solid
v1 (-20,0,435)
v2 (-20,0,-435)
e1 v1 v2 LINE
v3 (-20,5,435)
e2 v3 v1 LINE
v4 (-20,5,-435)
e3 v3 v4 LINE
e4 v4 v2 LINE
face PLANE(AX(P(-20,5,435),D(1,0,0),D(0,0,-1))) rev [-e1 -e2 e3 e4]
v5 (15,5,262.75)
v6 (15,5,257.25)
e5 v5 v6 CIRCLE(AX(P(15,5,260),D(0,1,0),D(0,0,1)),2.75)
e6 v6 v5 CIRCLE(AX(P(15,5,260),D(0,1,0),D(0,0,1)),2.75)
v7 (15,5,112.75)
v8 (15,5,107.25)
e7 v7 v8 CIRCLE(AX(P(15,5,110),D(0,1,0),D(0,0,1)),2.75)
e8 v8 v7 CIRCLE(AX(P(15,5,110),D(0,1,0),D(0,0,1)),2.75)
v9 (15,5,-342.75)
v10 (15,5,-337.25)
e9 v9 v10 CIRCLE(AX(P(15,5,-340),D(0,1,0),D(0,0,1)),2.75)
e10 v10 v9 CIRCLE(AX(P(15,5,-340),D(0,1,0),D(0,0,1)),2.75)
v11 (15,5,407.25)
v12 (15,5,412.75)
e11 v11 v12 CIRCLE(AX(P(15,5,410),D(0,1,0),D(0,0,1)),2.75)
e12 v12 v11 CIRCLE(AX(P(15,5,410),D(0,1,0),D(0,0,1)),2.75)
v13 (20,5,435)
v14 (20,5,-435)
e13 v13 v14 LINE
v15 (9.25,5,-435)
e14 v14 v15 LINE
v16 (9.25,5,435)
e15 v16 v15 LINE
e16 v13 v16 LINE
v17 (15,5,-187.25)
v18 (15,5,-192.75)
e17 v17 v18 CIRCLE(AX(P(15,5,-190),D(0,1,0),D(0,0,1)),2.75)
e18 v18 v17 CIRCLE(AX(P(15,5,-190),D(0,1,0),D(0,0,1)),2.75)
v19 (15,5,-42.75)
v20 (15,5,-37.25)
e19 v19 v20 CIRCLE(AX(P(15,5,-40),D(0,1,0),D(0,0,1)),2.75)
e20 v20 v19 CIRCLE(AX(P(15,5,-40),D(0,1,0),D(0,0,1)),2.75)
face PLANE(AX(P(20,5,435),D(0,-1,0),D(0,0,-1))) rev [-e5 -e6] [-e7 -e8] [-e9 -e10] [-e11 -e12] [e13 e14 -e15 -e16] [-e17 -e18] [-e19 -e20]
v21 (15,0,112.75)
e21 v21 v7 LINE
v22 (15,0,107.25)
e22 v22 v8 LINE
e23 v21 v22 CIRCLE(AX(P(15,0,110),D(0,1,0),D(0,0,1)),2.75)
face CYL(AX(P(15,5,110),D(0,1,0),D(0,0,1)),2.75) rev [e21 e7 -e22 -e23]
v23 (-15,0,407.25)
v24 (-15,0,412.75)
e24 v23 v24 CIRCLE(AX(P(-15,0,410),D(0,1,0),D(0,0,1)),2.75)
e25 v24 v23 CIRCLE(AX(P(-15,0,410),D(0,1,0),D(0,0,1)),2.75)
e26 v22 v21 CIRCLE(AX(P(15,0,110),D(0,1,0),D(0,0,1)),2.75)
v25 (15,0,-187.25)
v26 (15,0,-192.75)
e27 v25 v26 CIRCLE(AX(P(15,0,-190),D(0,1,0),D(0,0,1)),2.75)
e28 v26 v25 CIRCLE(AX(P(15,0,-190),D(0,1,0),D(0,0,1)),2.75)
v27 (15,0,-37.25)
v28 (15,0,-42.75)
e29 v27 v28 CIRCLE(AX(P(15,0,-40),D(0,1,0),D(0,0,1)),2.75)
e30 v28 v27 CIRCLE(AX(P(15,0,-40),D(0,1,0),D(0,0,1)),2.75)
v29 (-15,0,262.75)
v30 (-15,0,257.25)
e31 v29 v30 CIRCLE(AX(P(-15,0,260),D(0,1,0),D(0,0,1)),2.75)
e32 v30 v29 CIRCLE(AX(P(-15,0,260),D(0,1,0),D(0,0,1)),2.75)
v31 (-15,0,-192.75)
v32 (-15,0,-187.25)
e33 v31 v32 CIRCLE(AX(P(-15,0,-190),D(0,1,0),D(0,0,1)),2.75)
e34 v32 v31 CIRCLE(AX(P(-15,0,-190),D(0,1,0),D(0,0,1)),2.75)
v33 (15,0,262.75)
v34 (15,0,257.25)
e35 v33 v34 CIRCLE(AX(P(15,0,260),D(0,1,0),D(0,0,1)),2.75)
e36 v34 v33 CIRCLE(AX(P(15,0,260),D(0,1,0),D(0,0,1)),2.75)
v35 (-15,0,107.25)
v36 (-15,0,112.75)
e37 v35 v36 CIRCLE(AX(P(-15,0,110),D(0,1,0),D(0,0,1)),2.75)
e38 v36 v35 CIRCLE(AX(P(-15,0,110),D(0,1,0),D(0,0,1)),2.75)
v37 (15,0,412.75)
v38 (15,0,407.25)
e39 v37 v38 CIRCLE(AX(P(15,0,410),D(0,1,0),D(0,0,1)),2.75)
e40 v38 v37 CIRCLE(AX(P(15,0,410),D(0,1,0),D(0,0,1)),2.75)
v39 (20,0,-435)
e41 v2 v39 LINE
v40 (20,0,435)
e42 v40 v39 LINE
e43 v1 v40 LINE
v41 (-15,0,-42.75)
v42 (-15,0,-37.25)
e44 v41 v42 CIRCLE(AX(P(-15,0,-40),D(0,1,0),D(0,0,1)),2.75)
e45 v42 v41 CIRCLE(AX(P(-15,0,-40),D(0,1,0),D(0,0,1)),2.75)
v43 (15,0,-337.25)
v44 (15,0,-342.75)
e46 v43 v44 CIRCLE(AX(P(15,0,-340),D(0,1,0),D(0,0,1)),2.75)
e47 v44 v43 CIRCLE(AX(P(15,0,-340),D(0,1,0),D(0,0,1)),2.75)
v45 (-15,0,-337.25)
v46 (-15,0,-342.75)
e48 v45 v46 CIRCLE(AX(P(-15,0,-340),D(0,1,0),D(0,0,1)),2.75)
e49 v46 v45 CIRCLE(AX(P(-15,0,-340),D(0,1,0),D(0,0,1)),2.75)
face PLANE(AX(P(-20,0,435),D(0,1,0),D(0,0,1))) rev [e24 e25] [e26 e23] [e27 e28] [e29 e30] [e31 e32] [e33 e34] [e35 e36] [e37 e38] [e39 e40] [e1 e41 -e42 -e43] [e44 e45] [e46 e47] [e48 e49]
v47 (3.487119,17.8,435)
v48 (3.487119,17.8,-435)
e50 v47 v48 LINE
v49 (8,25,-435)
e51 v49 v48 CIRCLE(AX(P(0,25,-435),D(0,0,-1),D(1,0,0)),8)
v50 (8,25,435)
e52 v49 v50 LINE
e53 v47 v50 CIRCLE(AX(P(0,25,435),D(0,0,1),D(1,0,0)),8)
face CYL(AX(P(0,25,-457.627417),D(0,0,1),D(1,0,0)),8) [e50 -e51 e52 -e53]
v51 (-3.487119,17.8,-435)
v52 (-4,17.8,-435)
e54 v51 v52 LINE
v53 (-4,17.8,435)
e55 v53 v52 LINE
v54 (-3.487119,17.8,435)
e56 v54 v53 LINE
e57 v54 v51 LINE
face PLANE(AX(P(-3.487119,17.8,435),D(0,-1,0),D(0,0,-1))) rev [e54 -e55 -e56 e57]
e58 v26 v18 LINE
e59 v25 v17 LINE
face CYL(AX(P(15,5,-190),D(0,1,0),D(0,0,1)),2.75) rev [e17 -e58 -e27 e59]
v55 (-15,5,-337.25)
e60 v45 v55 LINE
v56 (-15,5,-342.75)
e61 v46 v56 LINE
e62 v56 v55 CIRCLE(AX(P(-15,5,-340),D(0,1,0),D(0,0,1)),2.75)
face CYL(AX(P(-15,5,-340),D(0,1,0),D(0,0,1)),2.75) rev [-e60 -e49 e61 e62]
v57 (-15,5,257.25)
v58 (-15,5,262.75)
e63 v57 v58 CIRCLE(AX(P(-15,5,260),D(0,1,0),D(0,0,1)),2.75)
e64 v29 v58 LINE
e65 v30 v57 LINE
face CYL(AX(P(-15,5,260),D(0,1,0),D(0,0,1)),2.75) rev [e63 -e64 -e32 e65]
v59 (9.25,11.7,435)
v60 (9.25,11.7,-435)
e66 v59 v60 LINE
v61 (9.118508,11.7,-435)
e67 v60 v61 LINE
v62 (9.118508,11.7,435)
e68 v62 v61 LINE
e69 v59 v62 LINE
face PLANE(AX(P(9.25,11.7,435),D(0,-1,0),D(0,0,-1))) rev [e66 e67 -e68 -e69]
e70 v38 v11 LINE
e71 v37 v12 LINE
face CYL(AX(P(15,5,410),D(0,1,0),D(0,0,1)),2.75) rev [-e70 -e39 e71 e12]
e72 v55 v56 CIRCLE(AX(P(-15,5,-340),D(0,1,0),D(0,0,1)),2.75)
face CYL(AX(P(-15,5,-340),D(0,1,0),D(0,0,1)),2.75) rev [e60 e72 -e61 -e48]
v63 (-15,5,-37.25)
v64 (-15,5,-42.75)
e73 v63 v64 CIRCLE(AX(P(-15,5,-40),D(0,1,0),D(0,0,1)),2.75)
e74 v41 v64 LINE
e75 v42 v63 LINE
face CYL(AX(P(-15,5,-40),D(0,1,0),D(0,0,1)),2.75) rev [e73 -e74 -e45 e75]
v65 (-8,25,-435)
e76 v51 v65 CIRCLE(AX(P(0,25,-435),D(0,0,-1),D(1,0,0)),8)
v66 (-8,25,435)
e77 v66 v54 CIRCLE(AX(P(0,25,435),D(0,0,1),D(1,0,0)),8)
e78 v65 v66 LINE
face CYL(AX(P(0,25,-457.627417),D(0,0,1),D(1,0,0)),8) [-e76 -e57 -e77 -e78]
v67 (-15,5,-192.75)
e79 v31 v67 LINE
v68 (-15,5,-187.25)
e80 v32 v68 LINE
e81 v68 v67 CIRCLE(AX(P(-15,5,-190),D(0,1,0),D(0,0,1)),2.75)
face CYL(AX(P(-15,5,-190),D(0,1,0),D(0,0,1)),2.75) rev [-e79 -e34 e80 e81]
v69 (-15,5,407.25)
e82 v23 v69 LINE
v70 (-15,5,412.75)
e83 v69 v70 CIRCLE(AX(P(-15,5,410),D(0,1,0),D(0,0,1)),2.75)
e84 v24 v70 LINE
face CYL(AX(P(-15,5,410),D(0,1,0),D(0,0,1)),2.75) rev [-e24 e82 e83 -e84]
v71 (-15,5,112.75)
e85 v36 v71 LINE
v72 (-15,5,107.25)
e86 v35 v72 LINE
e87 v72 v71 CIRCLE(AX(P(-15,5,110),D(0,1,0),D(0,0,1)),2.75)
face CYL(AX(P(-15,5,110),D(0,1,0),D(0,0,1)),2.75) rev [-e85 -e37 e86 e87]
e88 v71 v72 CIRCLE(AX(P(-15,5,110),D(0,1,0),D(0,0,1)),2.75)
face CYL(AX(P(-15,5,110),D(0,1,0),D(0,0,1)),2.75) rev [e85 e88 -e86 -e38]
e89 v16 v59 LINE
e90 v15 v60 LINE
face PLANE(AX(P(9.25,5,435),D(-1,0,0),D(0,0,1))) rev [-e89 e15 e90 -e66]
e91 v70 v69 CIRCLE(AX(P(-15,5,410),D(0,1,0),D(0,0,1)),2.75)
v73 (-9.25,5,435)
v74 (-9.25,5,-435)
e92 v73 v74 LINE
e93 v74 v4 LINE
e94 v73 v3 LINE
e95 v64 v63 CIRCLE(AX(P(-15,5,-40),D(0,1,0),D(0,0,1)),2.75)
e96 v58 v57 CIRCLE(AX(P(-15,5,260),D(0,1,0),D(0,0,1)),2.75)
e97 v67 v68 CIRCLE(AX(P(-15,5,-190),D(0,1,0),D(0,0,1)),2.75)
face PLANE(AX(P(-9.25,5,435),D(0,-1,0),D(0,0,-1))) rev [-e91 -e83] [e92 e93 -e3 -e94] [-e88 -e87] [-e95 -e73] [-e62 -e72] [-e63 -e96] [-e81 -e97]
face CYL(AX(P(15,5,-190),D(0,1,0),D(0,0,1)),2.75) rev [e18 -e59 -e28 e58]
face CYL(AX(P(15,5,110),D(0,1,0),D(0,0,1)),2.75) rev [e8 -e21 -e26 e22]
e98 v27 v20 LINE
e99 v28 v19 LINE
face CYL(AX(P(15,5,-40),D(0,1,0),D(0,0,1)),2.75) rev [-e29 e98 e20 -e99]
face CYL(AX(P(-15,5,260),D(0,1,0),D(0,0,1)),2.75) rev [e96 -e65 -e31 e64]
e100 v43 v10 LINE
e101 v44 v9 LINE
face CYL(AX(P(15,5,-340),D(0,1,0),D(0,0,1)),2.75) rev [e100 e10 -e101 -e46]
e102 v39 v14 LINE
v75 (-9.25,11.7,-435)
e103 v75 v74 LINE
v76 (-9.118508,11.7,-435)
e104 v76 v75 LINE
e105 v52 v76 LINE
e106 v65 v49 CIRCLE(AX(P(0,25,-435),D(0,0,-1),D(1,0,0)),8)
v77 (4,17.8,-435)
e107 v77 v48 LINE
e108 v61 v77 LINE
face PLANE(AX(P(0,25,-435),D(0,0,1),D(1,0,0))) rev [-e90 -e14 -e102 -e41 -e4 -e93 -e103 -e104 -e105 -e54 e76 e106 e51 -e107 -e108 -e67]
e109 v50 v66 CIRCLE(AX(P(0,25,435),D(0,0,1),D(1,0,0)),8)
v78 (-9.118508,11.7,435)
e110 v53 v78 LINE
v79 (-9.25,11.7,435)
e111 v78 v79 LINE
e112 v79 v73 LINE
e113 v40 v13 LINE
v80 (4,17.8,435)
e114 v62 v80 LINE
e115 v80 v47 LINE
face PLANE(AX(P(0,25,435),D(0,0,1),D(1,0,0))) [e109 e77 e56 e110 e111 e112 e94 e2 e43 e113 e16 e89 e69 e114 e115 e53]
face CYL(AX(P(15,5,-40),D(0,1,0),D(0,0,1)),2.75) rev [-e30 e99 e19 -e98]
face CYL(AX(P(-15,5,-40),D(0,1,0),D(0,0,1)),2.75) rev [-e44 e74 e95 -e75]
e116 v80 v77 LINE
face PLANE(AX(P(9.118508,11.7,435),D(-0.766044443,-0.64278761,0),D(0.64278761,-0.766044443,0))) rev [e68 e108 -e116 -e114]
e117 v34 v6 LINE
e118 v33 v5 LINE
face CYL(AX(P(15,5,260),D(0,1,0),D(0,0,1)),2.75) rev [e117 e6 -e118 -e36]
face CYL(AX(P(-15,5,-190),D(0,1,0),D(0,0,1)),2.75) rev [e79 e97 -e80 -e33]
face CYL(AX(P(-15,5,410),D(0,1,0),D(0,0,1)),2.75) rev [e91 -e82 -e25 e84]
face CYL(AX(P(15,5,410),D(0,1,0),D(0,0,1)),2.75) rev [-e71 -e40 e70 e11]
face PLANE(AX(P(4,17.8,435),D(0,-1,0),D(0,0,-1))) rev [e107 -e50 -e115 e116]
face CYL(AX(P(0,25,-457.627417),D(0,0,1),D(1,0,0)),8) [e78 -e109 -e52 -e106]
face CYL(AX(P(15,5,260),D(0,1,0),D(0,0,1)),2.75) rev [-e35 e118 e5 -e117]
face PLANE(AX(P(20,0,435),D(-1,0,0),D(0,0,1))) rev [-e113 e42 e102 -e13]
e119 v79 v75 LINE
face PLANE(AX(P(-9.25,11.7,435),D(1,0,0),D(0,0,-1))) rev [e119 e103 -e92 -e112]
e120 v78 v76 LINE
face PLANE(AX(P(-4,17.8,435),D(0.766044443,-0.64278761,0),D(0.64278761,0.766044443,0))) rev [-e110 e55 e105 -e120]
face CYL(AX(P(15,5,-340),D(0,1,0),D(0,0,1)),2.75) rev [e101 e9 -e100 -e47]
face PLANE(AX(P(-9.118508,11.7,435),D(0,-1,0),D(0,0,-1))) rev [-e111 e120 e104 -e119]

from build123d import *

# Parameters (mm, degrees)
EXTRUDE_1_DEPTH                  = 435
EXTRUDE_2_DEPTH                  = 870
HOLE_WIZARD_5_5_5_5_1_AT_2_COUNT = 2
HOLE_WIZARD_5_5_5_5_1_AT_2_PITCH = 30
PATTERN_LINEAR_1_COUNT           = 6
PATTERN_LINEAR_1_PITCH           = 150


with BuildPart() as part:
    # 草图1 → 凸台-拉伸1 (new, symmetric)
    with BuildSketch(Plane.XY):
        with BuildLine():
            Line((-9.25, 11.7), (-9.25, 5))
            Line((-9.25, 5), (-20, 5))
            Line((-20, 5), (-20, 0))
            Line((-20, 0), (20, 0))
            Line((20, 0), (20, 5))
            Line((20, 5), (9.25, 5))
            Line((9.25, 5), (9.25, 11.7))
            Line((9.25, 11.7), (9.11850775, 11.7))
            Line((9.11850775, 11.7), (4, 17.8))
            Line((4, 17.8), (3.487119155, 17.8))
            ThreePointArc((3.487119155, 17.8), (0, 17), (-3.487119155, 17.8))
            Line((-3.487119155, 17.8), (-4, 17.8))
            Line((-4, 17.8), (-9.11850775, 11.7))
            Line((-9.11850775, 11.7), (-9.25, 11.7))
        make_face()
    extrude(amount=EXTRUDE_1_DEPTH, both=True)

    # 草图2 → 凸台-拉伸2 (add)
    with BuildSketch(Plane.XY.offset(435)):
        with BuildLine():
            ThreePointArc((3.487119155, 17.8), (0, 33), (-3.487119155, 17.8))
            ThreePointArc((-3.487119155, 17.8), (0, 17), (3.487119155, 17.8))
        make_face()
    extrude(amount=-EXTRUDE_2_DEPTH)

    # 草图3 → Ø5.5 (5.5) 直径孔1 (revolve, cut)
    with BuildSketch(Plane(origin=(15, 5, 410), x_dir=(0, 0, 1), z_dir=(1, 0, 0))):
        Polygon((0, 0), (0, 17.19771324), (2.75, 15.61), (2.75, 0), align=None)
    hole_wizard_5_5_5_5_1 = revolve(axis=Axis((15, 11.35, 410), (0, -1, 0)), mode=Mode.SUBTRACT)

    # Ø5.5 (5.5) 直径孔1 at 2: Ø5.5 (5.5) 直径孔1 ×2
    with Locations(*[(-i * HOLE_WIZARD_5_5_5_5_1_AT_2_PITCH, 0, 0) for i in range(1, HOLE_WIZARD_5_5_5_5_1_AT_2_COUNT)]):
        add(hole_wizard_5_5_5_5_1, mode=Mode.SUBTRACT)

    # 阵列(线性)1: Ø5.5 (5.5) 直径孔1 ×6
    with Locations(*[(0, 0, -i * PATTERN_LINEAR_1_PITCH) for i in range(1, PATTERN_LINEAR_1_COUNT)]):
        add(hole_wizard_5_5_5_5_1, mode=Mode.SUBTRACT)

    # 阵列(线性)1 copy 1 sketch → 阵列(线性)1 copy 1 (revolve, cut)
    with BuildSketch(Plane(origin=(-15, 5, 260), x_dir=(0, 0, 1), z_dir=(1, 0, 0))):
        Polygon((0, 0), (0, 17.19771324), (2.75, 15.61), (2.75, 0), align=None)
    revolve(axis=Axis((-15, 11.35, 260), (0, -1, 0)), mode=Mode.SUBTRACT)

    # 阵列(线性)1 copy 2 sketch → 阵列(线性)1 copy 2 (revolve, cut)
    with BuildSketch(Plane(origin=(-15, 5, 110), x_dir=(0, 0, 1), z_dir=(1, 0, 0))):
        Polygon((0, 0), (0, 17.19771324), (2.75, 15.61), (2.75, 0), align=None)
    revolve(axis=Axis((-15, 11.35, 110), (0, -1, 0)), mode=Mode.SUBTRACT)

    # 阵列(线性)1 copy 3 sketch → 阵列(线性)1 copy 3 (revolve, cut)
    with BuildSketch(Plane(origin=(-15, 5, -40), x_dir=(0, 0, 1), z_dir=(1, 0, 0))):
        Polygon((0, 0), (0, 17.19771324), (2.75, 15.61), (2.75, 0), align=None)
    revolve(axis=Axis((-15, 11.35, -40), (0, -1, 0)), mode=Mode.SUBTRACT)

    # 阵列(线性)1 copy 4 sketch → 阵列(线性)1 copy 4 (revolve, cut)
    with BuildSketch(Plane(origin=(-15, 5, -190), x_dir=(0, 0, 1), z_dir=(1, 0, 0))):
        Polygon((0, 0), (0, 17.19771324), (2.75, 15.61), (2.75, 0), align=None)
    revolve(axis=Axis((-15, 11.35, -190), (0, -1, 0)), mode=Mode.SUBTRACT)

    # 阵列(线性)1 copy 5 sketch → 阵列(线性)1 copy 5 (revolve, cut)
    with BuildSketch(Plane(origin=(-15, 5, -340), x_dir=(0, 0, 1), z_dir=(1, 0, 0))):
        Polygon((0, 0), (0, 17.19771324), (2.75, 15.61), (2.75, 0), align=None)
    revolve(axis=Axis((-15, 11.35, -340), (0, -1, 0)), mode=Mode.SUBTRACT)


solid = part.part
